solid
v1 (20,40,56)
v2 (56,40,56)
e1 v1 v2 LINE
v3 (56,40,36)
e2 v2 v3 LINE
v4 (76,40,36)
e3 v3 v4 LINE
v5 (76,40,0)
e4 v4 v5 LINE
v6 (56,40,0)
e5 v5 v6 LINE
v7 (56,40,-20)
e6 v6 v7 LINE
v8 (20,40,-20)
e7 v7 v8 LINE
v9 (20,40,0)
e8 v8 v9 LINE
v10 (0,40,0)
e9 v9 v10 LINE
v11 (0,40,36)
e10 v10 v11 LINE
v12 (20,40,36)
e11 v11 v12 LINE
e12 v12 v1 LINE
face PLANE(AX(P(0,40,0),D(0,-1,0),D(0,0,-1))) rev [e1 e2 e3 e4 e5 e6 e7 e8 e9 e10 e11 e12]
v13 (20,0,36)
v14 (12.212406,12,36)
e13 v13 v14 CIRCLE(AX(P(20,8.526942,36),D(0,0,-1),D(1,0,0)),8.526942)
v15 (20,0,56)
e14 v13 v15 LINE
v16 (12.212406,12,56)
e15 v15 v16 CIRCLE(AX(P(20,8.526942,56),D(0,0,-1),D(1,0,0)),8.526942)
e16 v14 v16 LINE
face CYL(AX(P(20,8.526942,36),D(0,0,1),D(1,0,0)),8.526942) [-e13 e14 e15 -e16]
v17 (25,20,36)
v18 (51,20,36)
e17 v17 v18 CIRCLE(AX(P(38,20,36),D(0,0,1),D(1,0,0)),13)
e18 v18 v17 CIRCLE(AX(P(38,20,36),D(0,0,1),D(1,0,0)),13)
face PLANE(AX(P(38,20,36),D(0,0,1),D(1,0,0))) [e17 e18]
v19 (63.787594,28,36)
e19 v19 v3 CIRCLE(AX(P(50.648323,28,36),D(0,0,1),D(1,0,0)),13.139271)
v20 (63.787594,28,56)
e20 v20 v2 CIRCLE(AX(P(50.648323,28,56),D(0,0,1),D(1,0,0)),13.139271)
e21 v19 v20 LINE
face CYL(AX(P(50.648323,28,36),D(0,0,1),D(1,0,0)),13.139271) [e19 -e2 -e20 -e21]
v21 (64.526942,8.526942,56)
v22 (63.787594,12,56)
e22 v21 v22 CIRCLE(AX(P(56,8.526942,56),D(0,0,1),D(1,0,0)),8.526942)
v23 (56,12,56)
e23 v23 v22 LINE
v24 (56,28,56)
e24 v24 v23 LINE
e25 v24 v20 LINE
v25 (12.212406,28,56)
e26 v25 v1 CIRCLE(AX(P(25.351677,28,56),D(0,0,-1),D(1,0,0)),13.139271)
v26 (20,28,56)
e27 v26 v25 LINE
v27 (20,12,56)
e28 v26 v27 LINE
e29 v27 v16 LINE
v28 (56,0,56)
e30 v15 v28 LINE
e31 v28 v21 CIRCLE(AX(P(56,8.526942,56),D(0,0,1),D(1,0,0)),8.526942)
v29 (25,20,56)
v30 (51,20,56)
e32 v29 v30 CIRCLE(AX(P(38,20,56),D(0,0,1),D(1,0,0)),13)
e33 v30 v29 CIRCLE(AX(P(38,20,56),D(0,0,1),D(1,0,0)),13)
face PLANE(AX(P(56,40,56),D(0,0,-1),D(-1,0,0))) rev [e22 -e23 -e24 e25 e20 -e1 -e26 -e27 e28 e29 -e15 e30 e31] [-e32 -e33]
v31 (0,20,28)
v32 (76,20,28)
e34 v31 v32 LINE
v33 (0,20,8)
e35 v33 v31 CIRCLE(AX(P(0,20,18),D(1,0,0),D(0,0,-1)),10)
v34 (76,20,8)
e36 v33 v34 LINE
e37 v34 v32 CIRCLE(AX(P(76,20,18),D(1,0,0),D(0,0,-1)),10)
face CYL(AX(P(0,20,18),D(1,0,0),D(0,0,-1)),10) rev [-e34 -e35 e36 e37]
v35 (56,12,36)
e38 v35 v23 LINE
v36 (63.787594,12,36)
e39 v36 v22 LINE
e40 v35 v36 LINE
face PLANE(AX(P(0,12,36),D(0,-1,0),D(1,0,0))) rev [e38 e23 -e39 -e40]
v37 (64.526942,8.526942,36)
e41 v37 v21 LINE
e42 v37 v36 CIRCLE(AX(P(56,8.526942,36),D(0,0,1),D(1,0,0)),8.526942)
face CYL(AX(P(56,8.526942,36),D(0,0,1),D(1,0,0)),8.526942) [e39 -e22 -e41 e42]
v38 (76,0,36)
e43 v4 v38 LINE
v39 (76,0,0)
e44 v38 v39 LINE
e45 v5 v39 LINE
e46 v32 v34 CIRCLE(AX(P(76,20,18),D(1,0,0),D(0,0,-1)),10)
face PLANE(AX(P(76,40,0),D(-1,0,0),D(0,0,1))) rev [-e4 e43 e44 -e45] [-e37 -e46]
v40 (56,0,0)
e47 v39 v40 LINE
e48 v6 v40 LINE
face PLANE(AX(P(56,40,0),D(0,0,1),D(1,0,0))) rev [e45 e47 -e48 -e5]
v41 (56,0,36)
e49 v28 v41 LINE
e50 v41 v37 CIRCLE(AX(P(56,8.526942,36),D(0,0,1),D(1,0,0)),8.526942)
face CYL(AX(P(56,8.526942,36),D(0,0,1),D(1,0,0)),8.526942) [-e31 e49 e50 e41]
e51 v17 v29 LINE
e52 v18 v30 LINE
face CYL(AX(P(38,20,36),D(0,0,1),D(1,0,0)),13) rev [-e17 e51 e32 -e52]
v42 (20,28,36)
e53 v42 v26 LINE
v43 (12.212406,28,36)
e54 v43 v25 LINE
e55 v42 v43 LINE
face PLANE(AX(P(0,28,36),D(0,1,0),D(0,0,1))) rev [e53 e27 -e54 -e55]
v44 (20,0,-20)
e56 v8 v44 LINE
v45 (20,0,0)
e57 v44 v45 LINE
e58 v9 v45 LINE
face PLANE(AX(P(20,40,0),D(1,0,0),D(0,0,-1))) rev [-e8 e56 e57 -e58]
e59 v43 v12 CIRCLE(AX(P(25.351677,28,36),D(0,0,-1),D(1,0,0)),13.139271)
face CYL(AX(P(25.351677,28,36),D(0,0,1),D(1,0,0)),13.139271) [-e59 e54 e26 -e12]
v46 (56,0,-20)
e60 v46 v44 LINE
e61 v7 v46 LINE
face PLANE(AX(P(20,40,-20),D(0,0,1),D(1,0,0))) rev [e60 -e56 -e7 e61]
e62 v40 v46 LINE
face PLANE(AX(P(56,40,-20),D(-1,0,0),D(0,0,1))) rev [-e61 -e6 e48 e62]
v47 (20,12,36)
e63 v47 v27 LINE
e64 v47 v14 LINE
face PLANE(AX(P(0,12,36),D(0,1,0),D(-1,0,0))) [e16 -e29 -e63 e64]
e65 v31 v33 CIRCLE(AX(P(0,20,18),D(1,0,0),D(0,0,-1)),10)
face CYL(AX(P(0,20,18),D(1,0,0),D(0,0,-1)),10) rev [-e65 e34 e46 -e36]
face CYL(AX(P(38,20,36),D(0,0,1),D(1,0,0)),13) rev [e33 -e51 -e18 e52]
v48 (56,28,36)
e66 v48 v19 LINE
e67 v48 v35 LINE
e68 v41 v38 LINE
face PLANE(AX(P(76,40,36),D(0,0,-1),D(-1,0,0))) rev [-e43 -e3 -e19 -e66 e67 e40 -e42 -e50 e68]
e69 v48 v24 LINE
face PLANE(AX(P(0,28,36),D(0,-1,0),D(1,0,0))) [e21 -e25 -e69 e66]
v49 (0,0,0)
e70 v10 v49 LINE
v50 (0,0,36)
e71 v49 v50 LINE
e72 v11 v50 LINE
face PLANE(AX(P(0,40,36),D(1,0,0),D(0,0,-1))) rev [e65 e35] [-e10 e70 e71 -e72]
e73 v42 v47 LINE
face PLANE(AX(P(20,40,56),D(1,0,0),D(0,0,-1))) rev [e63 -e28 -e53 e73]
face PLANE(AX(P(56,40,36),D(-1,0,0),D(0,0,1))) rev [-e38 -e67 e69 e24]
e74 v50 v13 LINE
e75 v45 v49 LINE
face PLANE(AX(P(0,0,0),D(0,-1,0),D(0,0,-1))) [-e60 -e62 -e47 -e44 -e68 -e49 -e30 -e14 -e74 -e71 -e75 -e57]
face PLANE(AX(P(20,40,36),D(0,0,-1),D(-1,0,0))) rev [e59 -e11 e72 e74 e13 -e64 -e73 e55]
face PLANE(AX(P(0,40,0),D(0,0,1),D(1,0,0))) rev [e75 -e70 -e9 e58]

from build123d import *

# Parameters (mm, degrees)
CROSS_BLOCK_DEPTH      = 40
SIDE_LUG_DEPTH         = 20
BORE_26_SKETCH_R       = 13
BORE_26_DEPTH          = 20
CROSS_HOLE_20_SKETCH_R = 10
CROSS_HOLE_20_DEPTH    = 103.528044944


with BuildPart() as part:
    # Cross Profile Sketch → Cross Block (new body)
    with BuildSketch(Plane(origin=(0, 0, 0), x_dir=(1, 0, 0), z_dir=(0, 1, 0))):
        Polygon((0, 0), (20, 0), (20, 20), (56, 20), (56, 0), (76, 0), (76, -36), (56, -36), (56, -56), (20, -56), (20, -36), (0, -36), align=None)
    extrude(amount=CROSS_BLOCK_DEPTH)

    # Side Lug Sketch → Side Lug (add)
    with BuildSketch(Plane.XY.offset(56)):
        with BuildLine():
            Line((12.212406084, 28), (20, 28))
            Line((20, 28), (20, 40))
            ThreePointArc((20, 40), (14.32993543, 35.15273757), (12.212406084, 28))
        make_face()
        with BuildLine():
            Line((56, 40), (56, 28))
            Line((56, 28), (63.787593916, 28))
            ThreePointArc((63.787593916, 28), (61.67006457, 35.15273757), (56, 40))
        make_face()
        with BuildLine():
            Line((63.787593916, 12), (56, 12))
            Line((56, 12), (56, 0))
            ThreePointArc((56, 0), (63.15273757, 3.885057826), (63.787593916, 12))
        make_face()
        with BuildLine():
            Line((20, 0), (20, 12))
            Line((20, 12), (12.212406084, 12))
            ThreePointArc((12.212406084, 12), (12.84726243, 3.885057826), (20, 0))
        make_face()
    extrude(amount=-SIDE_LUG_DEPTH)

    # Bore Ø26 Sketch → Bore Ø26 (cut)
    with BuildSketch(Plane.XY.offset(56)):
        with Locations((38, 20)):
            Circle(BORE_26_SKETCH_R)
    extrude(amount=-BORE_26_DEPTH, mode=Mode.SUBTRACT)

    # Cross Hole Ø20 Sketch → Cross Hole Ø20 (cut, through all)
    with BuildSketch(Plane(origin=(76, 0, 0), x_dir=(0, 0, -1), z_dir=(1, 0, 0))):
        with Locations((-18, 20)):
            Circle(CROSS_HOLE_20_SKETCH_R)
    extrude(amount=-CROSS_HOLE_20_DEPTH, mode=Mode.SUBTRACT)


solid = part.part
